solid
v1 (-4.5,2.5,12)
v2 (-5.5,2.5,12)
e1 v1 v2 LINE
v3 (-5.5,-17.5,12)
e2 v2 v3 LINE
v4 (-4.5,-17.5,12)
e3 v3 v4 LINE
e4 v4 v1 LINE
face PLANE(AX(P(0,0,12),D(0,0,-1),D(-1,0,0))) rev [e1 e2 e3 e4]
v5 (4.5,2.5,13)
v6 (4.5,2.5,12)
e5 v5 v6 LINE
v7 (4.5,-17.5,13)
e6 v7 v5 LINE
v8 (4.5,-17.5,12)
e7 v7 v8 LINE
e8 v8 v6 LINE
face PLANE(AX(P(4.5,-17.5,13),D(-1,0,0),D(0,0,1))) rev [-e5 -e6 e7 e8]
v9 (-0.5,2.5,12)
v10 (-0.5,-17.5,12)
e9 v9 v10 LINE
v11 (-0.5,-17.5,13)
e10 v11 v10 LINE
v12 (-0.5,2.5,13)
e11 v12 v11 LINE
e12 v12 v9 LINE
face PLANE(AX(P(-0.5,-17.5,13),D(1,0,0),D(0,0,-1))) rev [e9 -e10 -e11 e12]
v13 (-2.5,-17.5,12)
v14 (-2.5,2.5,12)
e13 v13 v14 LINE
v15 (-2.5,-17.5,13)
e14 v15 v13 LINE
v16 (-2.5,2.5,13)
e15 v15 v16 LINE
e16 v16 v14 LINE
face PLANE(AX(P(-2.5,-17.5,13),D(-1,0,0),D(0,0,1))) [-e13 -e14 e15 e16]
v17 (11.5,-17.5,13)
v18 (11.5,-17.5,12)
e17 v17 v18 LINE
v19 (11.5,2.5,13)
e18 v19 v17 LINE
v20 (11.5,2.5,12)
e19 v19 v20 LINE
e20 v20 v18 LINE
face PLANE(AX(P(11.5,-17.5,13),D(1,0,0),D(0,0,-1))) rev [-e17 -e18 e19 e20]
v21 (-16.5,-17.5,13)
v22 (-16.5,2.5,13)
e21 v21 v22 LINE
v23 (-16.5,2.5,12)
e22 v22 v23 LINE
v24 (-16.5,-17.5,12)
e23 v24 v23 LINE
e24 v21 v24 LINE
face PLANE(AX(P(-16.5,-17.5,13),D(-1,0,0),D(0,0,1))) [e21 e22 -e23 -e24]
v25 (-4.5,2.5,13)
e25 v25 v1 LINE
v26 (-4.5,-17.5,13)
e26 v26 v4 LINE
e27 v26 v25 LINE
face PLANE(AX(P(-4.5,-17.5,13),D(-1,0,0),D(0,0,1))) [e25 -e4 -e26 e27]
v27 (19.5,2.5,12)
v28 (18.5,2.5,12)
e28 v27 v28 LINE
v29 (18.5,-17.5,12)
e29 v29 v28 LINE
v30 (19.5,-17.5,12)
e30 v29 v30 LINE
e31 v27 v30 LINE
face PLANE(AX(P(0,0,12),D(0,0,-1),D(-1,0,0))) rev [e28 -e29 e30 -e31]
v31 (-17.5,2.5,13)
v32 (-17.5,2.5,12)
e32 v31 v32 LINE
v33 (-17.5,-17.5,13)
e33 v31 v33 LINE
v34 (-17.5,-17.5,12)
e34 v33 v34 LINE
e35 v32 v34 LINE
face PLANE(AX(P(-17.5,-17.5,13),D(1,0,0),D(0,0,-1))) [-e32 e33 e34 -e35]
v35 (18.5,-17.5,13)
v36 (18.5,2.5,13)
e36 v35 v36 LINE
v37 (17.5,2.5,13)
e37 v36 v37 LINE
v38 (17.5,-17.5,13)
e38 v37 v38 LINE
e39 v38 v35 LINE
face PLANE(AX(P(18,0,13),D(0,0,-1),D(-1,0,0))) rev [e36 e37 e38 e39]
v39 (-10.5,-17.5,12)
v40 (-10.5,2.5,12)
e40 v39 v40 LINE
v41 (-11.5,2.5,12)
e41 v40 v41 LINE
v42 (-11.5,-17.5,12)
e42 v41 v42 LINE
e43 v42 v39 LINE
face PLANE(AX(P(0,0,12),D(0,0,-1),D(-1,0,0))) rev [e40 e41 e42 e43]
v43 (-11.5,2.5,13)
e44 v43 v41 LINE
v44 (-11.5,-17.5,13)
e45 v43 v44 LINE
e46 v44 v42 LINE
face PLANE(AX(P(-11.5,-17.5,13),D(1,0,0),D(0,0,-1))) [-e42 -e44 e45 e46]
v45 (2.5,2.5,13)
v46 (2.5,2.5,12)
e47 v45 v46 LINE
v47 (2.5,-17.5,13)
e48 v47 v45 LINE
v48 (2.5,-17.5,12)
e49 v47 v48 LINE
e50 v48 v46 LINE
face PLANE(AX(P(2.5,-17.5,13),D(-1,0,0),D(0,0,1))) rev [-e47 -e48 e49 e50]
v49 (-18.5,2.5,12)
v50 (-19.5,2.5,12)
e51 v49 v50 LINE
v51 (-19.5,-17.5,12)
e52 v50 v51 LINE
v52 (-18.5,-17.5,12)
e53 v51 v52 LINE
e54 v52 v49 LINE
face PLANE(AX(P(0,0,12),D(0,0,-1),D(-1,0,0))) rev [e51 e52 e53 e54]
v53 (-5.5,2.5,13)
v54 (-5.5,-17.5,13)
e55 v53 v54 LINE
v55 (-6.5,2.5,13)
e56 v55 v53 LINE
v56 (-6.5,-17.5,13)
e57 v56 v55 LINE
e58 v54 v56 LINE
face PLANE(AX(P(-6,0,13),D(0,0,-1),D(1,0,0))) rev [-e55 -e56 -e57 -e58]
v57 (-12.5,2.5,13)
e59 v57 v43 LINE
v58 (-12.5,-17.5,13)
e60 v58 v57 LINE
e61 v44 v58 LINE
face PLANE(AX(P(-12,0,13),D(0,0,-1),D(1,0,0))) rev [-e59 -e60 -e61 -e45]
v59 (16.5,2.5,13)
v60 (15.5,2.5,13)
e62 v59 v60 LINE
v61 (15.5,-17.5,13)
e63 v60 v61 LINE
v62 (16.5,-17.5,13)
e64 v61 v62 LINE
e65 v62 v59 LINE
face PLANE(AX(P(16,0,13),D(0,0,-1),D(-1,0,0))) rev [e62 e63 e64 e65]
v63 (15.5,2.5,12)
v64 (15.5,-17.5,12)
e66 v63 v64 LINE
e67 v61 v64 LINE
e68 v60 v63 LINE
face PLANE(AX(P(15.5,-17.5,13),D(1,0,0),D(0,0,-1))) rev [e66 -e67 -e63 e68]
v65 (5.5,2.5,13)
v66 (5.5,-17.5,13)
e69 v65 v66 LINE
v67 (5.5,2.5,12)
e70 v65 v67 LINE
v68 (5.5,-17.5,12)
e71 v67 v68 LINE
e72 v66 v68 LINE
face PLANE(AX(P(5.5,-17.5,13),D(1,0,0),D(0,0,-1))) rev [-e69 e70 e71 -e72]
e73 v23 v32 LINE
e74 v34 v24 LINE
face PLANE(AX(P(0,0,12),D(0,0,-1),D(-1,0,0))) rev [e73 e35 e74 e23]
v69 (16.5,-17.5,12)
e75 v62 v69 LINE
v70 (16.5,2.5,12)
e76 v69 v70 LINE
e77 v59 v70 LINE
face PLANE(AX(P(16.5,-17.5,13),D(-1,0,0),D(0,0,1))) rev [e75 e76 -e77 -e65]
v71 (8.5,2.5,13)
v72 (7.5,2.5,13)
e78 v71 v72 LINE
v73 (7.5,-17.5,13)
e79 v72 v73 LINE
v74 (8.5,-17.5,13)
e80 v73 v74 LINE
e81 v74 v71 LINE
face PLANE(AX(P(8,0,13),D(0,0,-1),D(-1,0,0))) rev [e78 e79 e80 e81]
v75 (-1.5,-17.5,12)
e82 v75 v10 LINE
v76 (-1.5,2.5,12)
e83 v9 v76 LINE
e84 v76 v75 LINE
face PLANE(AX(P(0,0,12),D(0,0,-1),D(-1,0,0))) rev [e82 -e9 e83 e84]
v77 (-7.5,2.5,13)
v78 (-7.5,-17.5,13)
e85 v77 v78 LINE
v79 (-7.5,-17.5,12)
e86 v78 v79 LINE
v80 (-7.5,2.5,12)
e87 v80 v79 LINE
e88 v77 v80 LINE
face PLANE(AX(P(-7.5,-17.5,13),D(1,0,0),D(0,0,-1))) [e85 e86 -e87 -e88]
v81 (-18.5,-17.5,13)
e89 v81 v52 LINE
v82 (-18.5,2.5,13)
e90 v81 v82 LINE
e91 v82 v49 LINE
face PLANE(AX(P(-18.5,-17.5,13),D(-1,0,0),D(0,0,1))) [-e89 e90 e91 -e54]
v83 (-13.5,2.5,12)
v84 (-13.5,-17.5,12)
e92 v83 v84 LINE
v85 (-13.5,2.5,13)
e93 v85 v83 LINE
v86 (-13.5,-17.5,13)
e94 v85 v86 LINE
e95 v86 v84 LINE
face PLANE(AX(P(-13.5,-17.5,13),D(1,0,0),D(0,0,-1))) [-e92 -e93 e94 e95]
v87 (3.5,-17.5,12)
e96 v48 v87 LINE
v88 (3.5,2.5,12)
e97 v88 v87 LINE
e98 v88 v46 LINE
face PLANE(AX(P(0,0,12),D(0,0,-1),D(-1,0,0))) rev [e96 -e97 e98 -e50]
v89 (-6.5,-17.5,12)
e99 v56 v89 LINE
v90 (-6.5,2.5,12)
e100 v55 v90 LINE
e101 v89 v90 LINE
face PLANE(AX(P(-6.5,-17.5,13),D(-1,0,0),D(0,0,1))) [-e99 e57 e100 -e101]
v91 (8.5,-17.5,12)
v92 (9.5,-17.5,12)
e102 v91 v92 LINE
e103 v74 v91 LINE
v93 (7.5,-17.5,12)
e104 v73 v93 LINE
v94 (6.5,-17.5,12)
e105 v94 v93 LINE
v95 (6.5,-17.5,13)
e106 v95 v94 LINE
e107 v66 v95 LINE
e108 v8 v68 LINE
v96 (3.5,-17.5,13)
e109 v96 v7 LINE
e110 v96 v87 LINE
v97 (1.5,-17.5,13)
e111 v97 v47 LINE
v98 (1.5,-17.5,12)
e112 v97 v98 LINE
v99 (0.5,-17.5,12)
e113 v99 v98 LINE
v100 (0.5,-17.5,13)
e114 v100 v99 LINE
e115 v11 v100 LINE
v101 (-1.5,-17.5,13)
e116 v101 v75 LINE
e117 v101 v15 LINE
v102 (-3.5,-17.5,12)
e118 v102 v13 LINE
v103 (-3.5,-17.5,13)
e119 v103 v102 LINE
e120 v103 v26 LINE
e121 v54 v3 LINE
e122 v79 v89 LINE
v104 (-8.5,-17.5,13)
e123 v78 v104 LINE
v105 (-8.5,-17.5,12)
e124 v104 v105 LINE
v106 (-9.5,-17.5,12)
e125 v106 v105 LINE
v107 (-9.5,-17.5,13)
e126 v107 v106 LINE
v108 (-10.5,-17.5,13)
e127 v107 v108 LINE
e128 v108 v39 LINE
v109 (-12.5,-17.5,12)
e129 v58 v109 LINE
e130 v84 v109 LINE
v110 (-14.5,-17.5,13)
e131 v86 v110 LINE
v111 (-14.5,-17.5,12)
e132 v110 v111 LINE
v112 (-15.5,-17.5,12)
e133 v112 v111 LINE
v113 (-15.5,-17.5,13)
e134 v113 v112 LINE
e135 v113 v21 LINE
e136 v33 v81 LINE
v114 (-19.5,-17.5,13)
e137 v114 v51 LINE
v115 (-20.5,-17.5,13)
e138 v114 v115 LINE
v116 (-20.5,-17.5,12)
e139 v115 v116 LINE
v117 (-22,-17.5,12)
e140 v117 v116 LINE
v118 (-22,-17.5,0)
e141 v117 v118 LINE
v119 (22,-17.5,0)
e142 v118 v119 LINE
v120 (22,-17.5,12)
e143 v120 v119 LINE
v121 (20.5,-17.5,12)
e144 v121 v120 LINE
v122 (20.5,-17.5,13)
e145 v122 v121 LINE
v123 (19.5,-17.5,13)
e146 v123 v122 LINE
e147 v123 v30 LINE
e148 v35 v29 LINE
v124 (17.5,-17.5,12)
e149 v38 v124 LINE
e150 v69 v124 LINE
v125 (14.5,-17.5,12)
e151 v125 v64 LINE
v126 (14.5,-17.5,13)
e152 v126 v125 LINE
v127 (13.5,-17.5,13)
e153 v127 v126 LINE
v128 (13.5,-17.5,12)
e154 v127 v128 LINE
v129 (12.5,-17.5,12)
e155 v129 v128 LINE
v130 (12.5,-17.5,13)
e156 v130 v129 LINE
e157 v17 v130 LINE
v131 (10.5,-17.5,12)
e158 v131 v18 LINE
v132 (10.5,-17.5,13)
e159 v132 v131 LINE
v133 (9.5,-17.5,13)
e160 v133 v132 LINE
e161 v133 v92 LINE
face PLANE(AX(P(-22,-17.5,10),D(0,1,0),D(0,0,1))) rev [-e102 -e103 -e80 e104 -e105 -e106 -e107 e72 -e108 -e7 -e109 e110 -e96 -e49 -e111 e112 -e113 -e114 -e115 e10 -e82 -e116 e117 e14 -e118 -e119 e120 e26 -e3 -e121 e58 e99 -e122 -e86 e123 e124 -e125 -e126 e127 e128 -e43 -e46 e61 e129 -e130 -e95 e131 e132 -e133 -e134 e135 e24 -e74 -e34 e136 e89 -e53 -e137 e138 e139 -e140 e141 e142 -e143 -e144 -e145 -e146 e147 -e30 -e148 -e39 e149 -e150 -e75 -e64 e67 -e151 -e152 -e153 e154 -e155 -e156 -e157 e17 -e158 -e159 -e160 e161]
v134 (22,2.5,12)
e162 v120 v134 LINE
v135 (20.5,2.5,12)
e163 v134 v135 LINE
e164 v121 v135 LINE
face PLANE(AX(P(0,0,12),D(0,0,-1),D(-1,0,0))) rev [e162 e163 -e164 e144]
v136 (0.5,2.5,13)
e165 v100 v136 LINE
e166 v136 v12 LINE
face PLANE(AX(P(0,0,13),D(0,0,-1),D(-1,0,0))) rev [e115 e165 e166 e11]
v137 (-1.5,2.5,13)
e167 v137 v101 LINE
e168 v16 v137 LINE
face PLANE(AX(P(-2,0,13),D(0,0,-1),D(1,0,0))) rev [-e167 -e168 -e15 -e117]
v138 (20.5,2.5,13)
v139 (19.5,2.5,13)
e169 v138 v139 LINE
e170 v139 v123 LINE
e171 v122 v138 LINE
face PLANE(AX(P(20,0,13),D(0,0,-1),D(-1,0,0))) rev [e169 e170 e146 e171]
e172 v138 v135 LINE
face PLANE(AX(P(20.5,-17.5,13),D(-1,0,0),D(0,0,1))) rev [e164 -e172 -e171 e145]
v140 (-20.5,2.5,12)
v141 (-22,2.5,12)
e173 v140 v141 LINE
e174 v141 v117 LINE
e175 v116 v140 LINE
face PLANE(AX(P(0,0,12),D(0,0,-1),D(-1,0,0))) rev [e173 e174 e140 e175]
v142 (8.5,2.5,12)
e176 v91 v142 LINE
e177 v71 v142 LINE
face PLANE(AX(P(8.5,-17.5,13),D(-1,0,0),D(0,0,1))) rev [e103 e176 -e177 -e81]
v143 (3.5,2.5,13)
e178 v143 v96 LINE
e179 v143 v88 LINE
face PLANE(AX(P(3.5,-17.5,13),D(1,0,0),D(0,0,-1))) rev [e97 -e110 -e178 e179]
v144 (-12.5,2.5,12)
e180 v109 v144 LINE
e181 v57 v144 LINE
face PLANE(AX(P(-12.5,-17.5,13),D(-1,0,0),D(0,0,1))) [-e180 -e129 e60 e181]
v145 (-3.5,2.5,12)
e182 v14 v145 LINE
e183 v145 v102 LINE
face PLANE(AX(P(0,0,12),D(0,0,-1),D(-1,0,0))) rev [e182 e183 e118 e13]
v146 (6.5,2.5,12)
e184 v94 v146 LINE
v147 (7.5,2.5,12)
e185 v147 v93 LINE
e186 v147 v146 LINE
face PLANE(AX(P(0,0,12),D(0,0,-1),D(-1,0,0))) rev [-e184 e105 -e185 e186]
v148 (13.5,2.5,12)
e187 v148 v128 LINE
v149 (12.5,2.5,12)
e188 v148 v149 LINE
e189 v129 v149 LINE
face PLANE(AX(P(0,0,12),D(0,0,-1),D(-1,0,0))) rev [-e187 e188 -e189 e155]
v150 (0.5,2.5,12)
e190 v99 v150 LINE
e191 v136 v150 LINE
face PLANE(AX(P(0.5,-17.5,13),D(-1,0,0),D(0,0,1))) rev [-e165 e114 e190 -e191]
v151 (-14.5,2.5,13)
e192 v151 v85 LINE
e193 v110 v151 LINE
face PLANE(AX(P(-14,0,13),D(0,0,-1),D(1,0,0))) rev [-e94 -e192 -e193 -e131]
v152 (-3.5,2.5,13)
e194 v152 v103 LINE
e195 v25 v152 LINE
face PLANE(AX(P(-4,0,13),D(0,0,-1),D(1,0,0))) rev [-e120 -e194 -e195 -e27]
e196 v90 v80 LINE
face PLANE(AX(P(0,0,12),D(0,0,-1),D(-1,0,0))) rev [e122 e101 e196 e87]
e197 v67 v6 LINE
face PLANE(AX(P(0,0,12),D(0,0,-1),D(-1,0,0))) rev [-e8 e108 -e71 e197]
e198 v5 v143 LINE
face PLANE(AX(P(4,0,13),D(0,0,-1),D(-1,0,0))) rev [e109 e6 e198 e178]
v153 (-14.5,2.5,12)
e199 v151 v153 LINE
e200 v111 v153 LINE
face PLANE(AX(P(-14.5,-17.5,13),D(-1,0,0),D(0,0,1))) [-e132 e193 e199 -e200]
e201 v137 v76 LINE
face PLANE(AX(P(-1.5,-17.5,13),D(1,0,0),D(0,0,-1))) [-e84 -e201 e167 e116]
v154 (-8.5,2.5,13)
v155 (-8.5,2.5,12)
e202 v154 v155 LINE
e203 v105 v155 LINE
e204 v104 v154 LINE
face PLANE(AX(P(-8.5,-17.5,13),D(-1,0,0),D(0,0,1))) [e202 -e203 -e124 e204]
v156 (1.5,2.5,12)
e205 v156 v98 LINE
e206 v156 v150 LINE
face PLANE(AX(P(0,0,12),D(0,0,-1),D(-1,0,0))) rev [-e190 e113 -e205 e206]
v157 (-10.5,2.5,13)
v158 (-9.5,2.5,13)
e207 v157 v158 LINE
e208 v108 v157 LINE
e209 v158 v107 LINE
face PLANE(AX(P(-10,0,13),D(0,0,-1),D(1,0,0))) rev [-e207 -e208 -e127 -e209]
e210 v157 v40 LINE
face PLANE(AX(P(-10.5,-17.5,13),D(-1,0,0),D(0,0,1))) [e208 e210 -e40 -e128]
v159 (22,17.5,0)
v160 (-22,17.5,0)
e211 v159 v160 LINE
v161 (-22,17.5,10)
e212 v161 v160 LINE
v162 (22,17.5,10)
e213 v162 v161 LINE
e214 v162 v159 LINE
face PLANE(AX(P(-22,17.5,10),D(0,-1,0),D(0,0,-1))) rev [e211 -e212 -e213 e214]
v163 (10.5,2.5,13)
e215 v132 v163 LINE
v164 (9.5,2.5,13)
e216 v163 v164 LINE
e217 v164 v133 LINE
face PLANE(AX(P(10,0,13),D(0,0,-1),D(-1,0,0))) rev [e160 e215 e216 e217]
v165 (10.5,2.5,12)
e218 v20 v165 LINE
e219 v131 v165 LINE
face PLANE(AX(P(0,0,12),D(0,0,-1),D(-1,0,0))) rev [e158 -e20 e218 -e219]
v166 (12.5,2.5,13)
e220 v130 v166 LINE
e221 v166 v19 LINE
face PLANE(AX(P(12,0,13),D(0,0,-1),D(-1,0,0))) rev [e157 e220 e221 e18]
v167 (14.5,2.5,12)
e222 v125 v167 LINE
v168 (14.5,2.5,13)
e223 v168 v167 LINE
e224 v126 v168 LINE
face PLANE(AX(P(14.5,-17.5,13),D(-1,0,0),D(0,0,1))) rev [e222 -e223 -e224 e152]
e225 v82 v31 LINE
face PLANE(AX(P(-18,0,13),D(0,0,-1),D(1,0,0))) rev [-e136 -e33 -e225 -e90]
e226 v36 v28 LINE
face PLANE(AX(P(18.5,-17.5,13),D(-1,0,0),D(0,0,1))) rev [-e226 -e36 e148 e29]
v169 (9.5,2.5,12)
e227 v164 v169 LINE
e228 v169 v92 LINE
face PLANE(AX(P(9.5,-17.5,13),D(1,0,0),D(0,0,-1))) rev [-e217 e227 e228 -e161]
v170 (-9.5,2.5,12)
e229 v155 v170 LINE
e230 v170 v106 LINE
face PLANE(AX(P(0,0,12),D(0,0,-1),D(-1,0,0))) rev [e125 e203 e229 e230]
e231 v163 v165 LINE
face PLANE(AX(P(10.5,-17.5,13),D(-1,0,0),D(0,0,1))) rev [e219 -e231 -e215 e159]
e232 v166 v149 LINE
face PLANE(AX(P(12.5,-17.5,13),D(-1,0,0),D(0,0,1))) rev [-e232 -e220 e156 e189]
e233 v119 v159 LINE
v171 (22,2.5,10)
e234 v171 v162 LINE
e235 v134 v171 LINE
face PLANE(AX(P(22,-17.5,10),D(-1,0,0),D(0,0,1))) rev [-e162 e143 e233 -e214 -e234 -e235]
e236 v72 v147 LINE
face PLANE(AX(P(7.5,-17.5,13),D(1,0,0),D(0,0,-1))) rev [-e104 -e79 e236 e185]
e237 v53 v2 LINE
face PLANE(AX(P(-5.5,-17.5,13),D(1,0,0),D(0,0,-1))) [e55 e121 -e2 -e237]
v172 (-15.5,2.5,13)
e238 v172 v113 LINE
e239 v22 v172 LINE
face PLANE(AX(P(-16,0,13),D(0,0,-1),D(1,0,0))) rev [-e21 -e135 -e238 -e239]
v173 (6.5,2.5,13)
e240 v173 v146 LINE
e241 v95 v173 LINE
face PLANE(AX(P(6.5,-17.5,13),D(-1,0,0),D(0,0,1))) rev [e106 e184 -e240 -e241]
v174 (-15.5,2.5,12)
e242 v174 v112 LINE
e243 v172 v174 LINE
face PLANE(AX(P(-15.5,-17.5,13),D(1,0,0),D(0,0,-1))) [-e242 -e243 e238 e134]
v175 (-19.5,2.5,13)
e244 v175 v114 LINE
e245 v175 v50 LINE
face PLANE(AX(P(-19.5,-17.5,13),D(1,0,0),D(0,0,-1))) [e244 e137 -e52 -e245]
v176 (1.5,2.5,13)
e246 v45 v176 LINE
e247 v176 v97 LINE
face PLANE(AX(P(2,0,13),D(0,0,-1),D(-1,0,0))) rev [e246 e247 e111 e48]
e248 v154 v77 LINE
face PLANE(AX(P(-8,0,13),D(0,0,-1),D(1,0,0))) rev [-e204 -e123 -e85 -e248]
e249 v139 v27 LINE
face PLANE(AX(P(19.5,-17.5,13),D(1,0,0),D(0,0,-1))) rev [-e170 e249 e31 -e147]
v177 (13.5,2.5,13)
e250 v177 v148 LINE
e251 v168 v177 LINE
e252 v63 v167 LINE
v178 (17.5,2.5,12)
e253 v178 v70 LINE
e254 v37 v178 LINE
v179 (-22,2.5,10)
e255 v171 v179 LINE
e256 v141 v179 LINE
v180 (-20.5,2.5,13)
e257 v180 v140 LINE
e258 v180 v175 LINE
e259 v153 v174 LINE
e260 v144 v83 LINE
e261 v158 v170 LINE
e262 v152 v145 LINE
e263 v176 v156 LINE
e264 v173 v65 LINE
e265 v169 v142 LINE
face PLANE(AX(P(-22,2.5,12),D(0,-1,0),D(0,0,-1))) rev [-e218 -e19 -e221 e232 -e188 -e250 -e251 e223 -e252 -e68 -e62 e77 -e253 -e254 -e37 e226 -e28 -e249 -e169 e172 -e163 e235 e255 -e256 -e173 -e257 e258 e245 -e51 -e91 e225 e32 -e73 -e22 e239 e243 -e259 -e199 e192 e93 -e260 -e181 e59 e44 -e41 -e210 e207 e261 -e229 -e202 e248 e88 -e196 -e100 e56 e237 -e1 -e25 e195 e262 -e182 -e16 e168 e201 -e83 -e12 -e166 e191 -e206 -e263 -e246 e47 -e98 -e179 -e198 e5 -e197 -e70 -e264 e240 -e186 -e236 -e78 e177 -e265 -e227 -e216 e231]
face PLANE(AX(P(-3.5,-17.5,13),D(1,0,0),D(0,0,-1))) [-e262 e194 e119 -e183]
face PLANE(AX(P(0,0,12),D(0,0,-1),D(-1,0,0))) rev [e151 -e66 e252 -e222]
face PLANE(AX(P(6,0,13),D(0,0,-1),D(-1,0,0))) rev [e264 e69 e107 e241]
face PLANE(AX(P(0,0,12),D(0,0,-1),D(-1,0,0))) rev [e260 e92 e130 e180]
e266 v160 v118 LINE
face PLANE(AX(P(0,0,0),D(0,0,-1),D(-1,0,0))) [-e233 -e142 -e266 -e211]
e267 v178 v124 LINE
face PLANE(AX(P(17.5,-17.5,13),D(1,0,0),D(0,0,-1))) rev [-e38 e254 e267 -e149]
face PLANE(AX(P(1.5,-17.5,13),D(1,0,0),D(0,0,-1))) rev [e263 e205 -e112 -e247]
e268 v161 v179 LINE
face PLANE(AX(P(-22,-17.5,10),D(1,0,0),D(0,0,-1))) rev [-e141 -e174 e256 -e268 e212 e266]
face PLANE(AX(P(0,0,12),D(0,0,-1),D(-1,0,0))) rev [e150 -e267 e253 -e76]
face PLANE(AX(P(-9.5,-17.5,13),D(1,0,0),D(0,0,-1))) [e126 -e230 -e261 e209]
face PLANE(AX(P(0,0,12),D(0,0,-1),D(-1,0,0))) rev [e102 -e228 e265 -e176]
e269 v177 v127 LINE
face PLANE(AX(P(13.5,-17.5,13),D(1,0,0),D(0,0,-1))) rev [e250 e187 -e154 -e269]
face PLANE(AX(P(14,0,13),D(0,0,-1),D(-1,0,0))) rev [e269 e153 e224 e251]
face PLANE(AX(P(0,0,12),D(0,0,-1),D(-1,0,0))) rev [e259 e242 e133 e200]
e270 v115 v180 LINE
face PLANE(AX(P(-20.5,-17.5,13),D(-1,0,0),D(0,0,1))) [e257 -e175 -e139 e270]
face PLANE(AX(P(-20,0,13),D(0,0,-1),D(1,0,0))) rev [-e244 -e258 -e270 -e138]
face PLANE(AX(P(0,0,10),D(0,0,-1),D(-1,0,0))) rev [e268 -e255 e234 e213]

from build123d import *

# Parameters (mm, degrees)
SKETCH_1_W                = 44
SKETCH_1_H                = 35
EXTRUDE_1_DEPTH           = 10
SKETCH_2_W                = 44
SKETCH_2_H                = 20
EXTRUDE_2_DEPTH           = 2
SKETCH_4_W                = 1
SKETCH_4_H                = 20
EXTRUDE_3_DEPTH           = 1
PATTERN_LINEAR_1_COUNT    = 11
PATTERN_LINEAR_1_PITCH    = 2
MIRROR_1_COPY_1_SKETCH_W  = 1
MIRROR_1_COPY_1_SKETCH_H  = 20
MIRROR_1_COPY_1_DEPTH     = 1
MIRROR_1_COPY_2_SKETCH_W  = 1
MIRROR_1_COPY_2_SKETCH_H  = 20
MIRROR_1_COPY_2_DEPTH     = 1
MIRROR_1_COPY_3_SKETCH_W  = 1
MIRROR_1_COPY_3_SKETCH_H  = 20
MIRROR_1_COPY_3_DEPTH     = 1
MIRROR_1_COPY_4_SKETCH_W  = 1
MIRROR_1_COPY_4_SKETCH_H  = 20
MIRROR_1_COPY_4_DEPTH     = 1
MIRROR_1_COPY_5_SKETCH_W  = 1
MIRROR_1_COPY_5_SKETCH_H  = 20
MIRROR_1_COPY_5_DEPTH     = 1
MIRROR_1_COPY_6_SKETCH_W  = 1
MIRROR_1_COPY_6_SKETCH_H  = 20
MIRROR_1_COPY_6_DEPTH     = 1
MIRROR_1_COPY_7_SKETCH_W  = 1
MIRROR_1_COPY_7_SKETCH_H  = 20
MIRROR_1_COPY_7_DEPTH     = 1
MIRROR_1_COPY_8_SKETCH_W  = 1
MIRROR_1_COPY_8_SKETCH_H  = 20
MIRROR_1_COPY_8_DEPTH     = 1
MIRROR_1_COPY_9_SKETCH_W  = 1
MIRROR_1_COPY_9_SKETCH_H  = 20
MIRROR_1_COPY_9_DEPTH     = 1
MIRROR_1_COPY_10_SKETCH_W = 1
MIRROR_1_COPY_10_SKETCH_H = 20
MIRROR_1_COPY_10_DEPTH    = 1
MIRROR_1_COPY_11_SKETCH_W = 1
MIRROR_1_COPY_11_SKETCH_H = 20
MIRROR_1_COPY_11_DEPTH    = 1


with BuildPart() as part:
    # 草图1 → 凸台-拉伸1 (new body)
    with BuildSketch(Plane.XY):
        Rectangle(SKETCH_1_W, SKETCH_1_H)
    extrude(amount=EXTRUDE_1_DEPTH)

    # 草图2 → 凸台-拉伸2 (add)
    with BuildSketch(Plane.XY.offset(10)):
        with Locations((0, -7.5)):
            Rectangle(SKETCH_2_W, SKETCH_2_H)
    extrude(amount=EXTRUDE_2_DEPTH)

    # 草图4 → 凸台-拉伸3 (add)
    with BuildSketch(Plane.XY.offset(12)):
        with Locations((0, -7.5)):
            Rectangle(SKETCH_4_W, SKETCH_4_H)
    extrude_3 = extrude(amount=EXTRUDE_3_DEPTH)

    # 阵列(线性)1: 凸台-拉伸3 ×11
    with Locations(*[(i * PATTERN_LINEAR_1_PITCH, 0, 0) for i in range(1, PATTERN_LINEAR_1_COUNT)]):
        add(extrude_3)

    # 镜向1 copy 1 sketch → 镜向1 copy 1 (add)
    with BuildSketch(Plane(origin=(-2, 0, 12), x_dir=(-1, 0, 0), z_dir=(0, 0, 1))):
        with Locations((0, 7.5)):
            Rectangle(MIRROR_1_COPY_1_SKETCH_W, MIRROR_1_COPY_1_SKETCH_H)
    extrude(amount=MIRROR_1_COPY_1_DEPTH)

    # 镜向1 copy 2 sketch → 镜向1 copy 2 (add)
    with BuildSketch(Plane(origin=(-4, 0, 12), x_dir=(-1, 0, 0), z_dir=(0, 0, 1))):
        with Locations((0, 7.5)):
            Rectangle(MIRROR_1_COPY_2_SKETCH_W, MIRROR_1_COPY_2_SKETCH_H)
    extrude(amount=MIRROR_1_COPY_2_DEPTH)

    # 镜向1 copy 3 sketch → 镜向1 copy 3 (add)
    with BuildSketch(Plane(origin=(-6, 0, 12), x_dir=(-1, 0, 0), z_dir=(0, 0, 1))):
        with Locations((0, 7.5)):
            Rectangle(MIRROR_1_COPY_3_SKETCH_W, MIRROR_1_COPY_3_SKETCH_H)
    extrude(amount=MIRROR_1_COPY_3_DEPTH)

    # 镜向1 copy 4 sketch → 镜向1 copy 4 (add)
    with BuildSketch(Plane(origin=(-8, 0, 12), x_dir=(-1, 0, 0), z_dir=(0, 0, 1))):
        with Locations((0, 7.5)):
            Rectangle(MIRROR_1_COPY_4_SKETCH_W, MIRROR_1_COPY_4_SKETCH_H)
    extrude(amount=MIRROR_1_COPY_4_DEPTH)

    # 镜向1 copy 5 sketch → 镜向1 copy 5 (add)
    with BuildSketch(Plane(origin=(-10, 0, 12), x_dir=(-1, 0, 0), z_dir=(0, 0, 1))):
        with Locations((0, 7.5)):
            Rectangle(MIRROR_1_COPY_5_SKETCH_W, MIRROR_1_COPY_5_SKETCH_H)
    extrude(amount=MIRROR_1_COPY_5_DEPTH)

    # 镜向1 copy 6 sketch → 镜向1 copy 6 (add)
    with BuildSketch(Plane(origin=(-12, 0, 12), x_dir=(-1, 0, 0), z_dir=(0, 0, 1))):
        with Locations((0, 7.5)):
            Rectangle(MIRROR_1_COPY_6_SKETCH_W, MIRROR_1_COPY_6_SKETCH_H)
    extrude(amount=MIRROR_1_COPY_6_DEPTH)

    # 镜向1 copy 7 sketch → 镜向1 copy 7 (add)
    with BuildSketch(Plane(origin=(-14, 0, 12), x_dir=(-1, 0, 0), z_dir=(0, 0, 1))):
        with Locations((0, 7.5)):
            Rectangle(MIRROR_1_COPY_7_SKETCH_W, MIRROR_1_COPY_7_SKETCH_H)
    extrude(amount=MIRROR_1_COPY_7_DEPTH)

    # 镜向1 copy 8 sketch → 镜向1 copy 8 (add)
    with BuildSketch(Plane(origin=(-16, 0, 12), x_dir=(-1, 0, 0), z_dir=(0, 0, 1))):
        with Locations((0, 7.5)):
            Rectangle(MIRROR_1_COPY_8_SKETCH_W, MIRROR_1_COPY_8_SKETCH_H)
    extrude(amount=MIRROR_1_COPY_8_DEPTH)

    # 镜向1 copy 9 sketch → 镜向1 copy 9 (add)
    with BuildSketch(Plane(origin=(-18, 0, 12), x_dir=(-1, 0, 0), z_dir=(0, 0, 1))):
        with Locations((0, 7.5)):
            Rectangle(MIRROR_1_COPY_9_SKETCH_W, MIRROR_1_COPY_9_SKETCH_H)
    extrude(amount=MIRROR_1_COPY_9_DEPTH)

    # 镜向1 copy 10 sketch → 镜向1 copy 10 (add)
    with BuildSketch(Plane(origin=(-20, 0, 12), x_dir=(-1, 0, 0), z_dir=(0, 0, 1))):
        with Locations((0, 7.5)):
            Rectangle(MIRROR_1_COPY_10_SKETCH_W, MIRROR_1_COPY_10_SKETCH_H)
    extrude(amount=MIRROR_1_COPY_10_DEPTH)

    # 镜向1 copy 11 sketch → 镜向1 copy 11 (add)
    with BuildSketch(Plane(origin=(0, 0, 12), x_dir=(-1, 0, 0), z_dir=(0, 0, 1))):
        with Locations((0, 7.5)):
            Rectangle(MIRROR_1_COPY_11_SKETCH_W, MIRROR_1_COPY_11_SKETCH_H)
    extrude(amount=MIRROR_1_COPY_11_DEPTH)


solid = part.part
